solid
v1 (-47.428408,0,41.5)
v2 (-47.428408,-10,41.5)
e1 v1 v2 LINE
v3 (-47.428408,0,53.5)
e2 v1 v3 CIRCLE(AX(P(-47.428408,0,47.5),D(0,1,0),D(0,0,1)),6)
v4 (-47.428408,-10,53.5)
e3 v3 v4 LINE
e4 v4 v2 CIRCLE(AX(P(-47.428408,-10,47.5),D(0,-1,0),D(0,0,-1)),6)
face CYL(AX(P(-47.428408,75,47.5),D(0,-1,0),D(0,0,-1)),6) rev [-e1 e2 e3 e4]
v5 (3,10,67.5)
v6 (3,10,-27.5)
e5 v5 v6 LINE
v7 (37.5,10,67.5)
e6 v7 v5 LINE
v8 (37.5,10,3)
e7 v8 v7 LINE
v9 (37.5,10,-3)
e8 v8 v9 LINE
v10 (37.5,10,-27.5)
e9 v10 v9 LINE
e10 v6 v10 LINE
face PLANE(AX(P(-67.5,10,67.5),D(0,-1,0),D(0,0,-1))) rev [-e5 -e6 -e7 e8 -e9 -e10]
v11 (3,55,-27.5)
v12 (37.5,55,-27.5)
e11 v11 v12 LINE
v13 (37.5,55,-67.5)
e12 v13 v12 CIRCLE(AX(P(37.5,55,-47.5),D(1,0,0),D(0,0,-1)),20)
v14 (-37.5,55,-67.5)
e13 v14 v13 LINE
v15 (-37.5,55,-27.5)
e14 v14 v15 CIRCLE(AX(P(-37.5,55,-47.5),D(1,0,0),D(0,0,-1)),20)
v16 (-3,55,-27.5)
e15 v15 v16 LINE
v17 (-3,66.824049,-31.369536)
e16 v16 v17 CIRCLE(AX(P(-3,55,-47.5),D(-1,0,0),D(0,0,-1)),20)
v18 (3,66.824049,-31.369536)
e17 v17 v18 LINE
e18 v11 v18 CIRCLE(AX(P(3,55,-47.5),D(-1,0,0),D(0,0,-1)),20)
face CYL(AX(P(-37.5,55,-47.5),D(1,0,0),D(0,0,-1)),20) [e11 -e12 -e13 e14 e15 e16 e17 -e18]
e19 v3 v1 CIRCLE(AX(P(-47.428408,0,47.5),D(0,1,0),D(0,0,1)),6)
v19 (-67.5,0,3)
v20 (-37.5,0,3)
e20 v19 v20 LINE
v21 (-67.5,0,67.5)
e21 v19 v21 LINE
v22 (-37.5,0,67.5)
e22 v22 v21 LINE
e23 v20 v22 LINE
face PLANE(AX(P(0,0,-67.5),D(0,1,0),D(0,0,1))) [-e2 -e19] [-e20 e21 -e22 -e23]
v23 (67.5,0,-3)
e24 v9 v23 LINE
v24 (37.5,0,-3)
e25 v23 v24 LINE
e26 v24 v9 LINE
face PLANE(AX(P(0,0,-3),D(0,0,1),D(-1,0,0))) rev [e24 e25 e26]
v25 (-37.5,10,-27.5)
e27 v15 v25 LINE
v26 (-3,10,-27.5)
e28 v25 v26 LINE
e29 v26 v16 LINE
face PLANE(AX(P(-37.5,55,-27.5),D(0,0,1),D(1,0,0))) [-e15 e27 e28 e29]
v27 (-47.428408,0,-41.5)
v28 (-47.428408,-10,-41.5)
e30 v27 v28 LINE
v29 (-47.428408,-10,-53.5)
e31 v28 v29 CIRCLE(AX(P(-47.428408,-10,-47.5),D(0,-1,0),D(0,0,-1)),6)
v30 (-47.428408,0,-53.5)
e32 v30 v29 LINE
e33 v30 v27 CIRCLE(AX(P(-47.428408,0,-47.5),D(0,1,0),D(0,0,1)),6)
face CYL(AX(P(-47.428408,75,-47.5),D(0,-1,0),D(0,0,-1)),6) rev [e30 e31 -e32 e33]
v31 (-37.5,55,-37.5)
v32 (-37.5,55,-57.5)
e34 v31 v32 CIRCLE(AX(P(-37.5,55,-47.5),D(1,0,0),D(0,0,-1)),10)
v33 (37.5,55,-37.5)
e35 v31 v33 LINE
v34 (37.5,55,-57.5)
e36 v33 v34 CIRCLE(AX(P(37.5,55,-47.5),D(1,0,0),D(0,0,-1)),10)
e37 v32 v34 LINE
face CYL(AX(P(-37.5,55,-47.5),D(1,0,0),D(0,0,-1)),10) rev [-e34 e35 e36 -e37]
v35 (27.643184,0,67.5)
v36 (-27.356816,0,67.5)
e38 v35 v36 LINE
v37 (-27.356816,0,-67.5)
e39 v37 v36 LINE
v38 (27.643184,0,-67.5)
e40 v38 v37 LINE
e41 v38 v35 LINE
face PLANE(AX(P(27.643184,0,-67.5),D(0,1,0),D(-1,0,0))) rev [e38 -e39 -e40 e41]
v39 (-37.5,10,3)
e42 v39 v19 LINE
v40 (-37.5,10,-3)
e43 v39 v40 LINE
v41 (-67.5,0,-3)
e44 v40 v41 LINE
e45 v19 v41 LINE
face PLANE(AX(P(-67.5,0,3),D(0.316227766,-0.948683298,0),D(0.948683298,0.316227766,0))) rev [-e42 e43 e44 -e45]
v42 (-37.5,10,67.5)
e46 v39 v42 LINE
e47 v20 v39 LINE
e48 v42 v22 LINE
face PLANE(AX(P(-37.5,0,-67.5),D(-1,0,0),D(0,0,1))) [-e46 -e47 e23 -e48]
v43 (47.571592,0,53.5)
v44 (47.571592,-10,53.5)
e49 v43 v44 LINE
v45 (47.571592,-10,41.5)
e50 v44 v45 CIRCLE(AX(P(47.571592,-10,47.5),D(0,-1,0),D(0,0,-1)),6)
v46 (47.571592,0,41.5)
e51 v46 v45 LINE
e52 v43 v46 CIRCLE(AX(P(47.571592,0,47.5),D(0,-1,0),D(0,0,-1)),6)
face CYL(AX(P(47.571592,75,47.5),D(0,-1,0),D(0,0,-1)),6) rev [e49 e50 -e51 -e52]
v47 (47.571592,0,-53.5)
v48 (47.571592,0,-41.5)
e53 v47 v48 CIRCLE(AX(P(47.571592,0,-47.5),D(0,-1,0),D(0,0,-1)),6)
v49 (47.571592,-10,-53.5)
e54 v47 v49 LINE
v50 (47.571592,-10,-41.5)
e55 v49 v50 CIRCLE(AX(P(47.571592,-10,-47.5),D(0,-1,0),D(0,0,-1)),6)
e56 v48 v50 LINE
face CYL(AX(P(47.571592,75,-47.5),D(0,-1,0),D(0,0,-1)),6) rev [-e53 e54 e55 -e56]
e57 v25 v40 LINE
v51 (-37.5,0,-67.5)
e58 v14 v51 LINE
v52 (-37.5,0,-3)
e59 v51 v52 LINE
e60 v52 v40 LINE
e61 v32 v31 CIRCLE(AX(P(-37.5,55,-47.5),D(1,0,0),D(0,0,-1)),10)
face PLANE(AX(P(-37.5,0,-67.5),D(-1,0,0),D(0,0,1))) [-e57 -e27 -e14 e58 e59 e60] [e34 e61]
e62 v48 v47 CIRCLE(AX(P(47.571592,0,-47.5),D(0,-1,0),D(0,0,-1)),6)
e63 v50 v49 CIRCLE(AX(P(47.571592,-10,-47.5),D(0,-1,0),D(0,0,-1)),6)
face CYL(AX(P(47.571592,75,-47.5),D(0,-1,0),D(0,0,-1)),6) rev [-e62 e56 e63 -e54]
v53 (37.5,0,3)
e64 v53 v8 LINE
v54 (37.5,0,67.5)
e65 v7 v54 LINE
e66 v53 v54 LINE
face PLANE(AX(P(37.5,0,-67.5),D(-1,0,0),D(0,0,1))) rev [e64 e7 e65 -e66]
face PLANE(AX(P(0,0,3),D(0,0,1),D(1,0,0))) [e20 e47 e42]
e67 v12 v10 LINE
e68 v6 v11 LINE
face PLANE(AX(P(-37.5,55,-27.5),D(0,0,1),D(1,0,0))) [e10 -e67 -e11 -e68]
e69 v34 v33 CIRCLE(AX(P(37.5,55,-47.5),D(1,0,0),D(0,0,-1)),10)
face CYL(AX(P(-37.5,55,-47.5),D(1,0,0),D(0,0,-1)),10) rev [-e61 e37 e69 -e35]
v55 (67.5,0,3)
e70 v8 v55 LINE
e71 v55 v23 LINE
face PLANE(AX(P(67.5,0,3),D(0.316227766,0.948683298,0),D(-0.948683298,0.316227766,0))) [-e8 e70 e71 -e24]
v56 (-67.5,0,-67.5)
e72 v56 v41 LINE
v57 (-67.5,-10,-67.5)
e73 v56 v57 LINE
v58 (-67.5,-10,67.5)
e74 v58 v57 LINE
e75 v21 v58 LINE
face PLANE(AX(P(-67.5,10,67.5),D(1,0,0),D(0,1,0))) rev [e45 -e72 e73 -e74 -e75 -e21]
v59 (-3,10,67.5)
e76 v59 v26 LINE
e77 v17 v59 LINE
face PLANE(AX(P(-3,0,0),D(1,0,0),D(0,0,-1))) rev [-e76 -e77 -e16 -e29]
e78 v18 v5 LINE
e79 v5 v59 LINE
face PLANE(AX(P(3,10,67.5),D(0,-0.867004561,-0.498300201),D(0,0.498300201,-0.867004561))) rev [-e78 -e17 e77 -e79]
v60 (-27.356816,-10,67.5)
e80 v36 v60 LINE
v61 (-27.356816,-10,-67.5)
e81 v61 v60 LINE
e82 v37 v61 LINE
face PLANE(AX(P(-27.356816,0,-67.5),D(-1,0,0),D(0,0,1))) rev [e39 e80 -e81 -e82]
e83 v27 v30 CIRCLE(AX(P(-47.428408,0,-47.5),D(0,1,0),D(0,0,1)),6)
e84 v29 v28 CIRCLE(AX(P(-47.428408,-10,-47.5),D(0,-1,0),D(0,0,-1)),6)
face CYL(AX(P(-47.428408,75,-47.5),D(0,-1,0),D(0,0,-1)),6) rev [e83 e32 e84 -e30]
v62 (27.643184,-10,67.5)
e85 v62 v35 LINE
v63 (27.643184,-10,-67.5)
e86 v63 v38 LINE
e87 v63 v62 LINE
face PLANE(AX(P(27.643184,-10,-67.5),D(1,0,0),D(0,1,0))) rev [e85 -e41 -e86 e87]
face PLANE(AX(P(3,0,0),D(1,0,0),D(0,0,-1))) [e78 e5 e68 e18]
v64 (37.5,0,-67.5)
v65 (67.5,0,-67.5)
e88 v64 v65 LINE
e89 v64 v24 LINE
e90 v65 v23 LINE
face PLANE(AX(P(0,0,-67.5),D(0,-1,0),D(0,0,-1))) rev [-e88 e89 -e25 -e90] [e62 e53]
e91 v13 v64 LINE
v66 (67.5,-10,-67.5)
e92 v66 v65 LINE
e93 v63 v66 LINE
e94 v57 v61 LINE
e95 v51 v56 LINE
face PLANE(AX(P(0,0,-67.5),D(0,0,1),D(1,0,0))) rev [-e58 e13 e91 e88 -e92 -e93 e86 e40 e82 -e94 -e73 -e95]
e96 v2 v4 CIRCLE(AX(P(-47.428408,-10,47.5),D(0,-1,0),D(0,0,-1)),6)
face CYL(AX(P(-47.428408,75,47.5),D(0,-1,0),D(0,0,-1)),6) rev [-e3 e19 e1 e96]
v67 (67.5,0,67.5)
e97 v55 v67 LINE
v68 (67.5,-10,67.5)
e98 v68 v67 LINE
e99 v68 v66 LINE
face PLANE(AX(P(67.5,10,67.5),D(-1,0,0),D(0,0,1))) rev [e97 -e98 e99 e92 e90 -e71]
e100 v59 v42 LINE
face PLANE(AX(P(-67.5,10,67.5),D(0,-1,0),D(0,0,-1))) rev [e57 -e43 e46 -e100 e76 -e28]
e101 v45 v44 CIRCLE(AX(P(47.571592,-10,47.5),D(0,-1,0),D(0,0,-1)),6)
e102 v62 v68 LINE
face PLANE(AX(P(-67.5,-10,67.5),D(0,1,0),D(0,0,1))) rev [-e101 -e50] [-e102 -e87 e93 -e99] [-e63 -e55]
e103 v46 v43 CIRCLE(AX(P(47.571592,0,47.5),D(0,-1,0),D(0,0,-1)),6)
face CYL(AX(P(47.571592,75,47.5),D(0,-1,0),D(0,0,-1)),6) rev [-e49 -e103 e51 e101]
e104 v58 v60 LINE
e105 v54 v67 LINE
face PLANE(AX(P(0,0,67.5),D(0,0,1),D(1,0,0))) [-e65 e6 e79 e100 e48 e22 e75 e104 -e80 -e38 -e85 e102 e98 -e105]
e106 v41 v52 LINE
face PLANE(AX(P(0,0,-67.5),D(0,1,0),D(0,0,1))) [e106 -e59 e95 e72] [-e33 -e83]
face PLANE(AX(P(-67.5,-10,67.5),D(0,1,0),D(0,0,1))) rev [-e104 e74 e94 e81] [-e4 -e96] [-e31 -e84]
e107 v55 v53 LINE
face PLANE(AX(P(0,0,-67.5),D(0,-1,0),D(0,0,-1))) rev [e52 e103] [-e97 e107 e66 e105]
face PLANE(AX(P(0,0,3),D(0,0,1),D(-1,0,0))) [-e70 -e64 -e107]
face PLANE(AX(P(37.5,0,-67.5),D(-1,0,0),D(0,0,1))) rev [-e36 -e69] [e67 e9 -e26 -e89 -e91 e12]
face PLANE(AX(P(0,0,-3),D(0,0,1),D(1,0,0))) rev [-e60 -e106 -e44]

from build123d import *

# Parameters (mm, degrees)
BASE_PLATE_SKETCH_W     = 135
BASE_PLATE_SKETCH_H     = 20
BASE_PLATE_DEPTH        = 67.5
BOTTOM_CHANNEL_DEPTH    = 152.265495074
TOP_RECESS_SKETCH_W     = 30
TOP_RECESS_SKETCH_H     = 10
TOP_RECESS_DEPTH        = 152.265495074
UPRIGHT_LUG_SKETCH_R    = 10
UPRIGHT_LUG_DEPTH       = 75
SIDE_GUSSET_DEPTH       = 3
CENTRE_START            = -37.5
CENTRE_RIB_DEPTH        = 3
MOUNTING_HOLES_SKETCH_R = 6
MOUNTING_HOLES_12_DEPTH = 128.818230312


with BuildPart() as part:
    # Base Plate Sketch → Base Plate (new, symmetric)
    with BuildSketch(Plane.XY):
        Rectangle(BASE_PLATE_SKETCH_W, BASE_PLATE_SKETCH_H)
    extrude(amount=BASE_PLATE_DEPTH, both=True)

    # Bottom Channel Sketch → Bottom Channel (cut, through all)
    with BuildSketch(Plane.XY.offset(67.5)):
        Polygon((27.643184154, 0), (0, 0), (-27.356815846, 0), (-27.356815846, -10), (27.643184154, -10), align=None)
    extrude(amount=-BOTTOM_CHANNEL_DEPTH, mode=Mode.SUBTRACT)

    # Top Recess Sketch → Top Recess (cut, through all)
    with BuildSketch(Plane.XY.offset(67.5)):
        with Locations((-52.5, 5)):
            Rectangle(TOP_RECESS_SKETCH_W, TOP_RECESS_SKETCH_H)
        with Locations((52.5, 5)):
            Rectangle(TOP_RECESS_SKETCH_W, TOP_RECESS_SKETCH_H)
    extrude(amount=-TOP_RECESS_DEPTH, mode=Mode.SUBTRACT)

    # Upright Lug Sketch → Upright Lug (add)
    with BuildSketch(Plane(origin=(37.5, 0, 0), x_dir=(0, 0, -1), z_dir=(1, 0, 0))):
        with BuildLine():
            Line((67.5, 10), (67.5, 55))
            ThreePointArc((67.5, 55), (47.5, 75), (27.5, 55))
            Line((27.5, 55), (27.5, 10))
            Line((27.5, 10), (67.5, 10))
        make_face()
        with Locations((47.5, 55)):
            Circle(UPRIGHT_LUG_SKETCH_R, mode=Mode.SUBTRACT)
    extrude(amount=-UPRIGHT_LUG_DEPTH)

    # Side Gusset Sketch → Side Gusset (add, symmetric)
    with BuildSketch(Plane.XY):
        Polygon((-67.5, 0), (-37.5, 10), (-37.5, 0), align=None)
    side_gusset = extrude(amount=SIDE_GUSSET_DEPTH, both=True)

    # Side Gusset Mirror: Side Gusset across plane
    add(side_gusset.mirror(Plane(origin=(0, 0, 0), x_dir=(0, 0, 1), z_dir=(1, 0, 0))))

    # Centre Rib Sketch → Centre Rib (add, symmetric)
    with BuildSketch(Plane(origin=(37.5, 0, 0), x_dir=(0, 0, -1), z_dir=(1, 0, 0)).offset(CENTRE_START)):
        Polygon((-67.5, 10), (35.500032612, 69.198001073), (35.500032612, 10), (29.449687004, 10), align=None)
    extrude(amount=CENTRE_RIB_DEPTH, both=True)

    # Mounting Holes Sketch → Mounting Holes Ø12 (cut, through all)
    with BuildSketch(Plane.XZ.offset(10)):
        with Locations(Location((47.571592077, -47.5, 0), (0, 0, 270))):
            Circle(MOUNTING_HOLES_SKETCH_R)
        with Locations(Location((-47.428407923, -47.5, 0), (0, 0, 270))):
            Circle(MOUNTING_HOLES_SKETCH_R)
        with Locations(Location((-47.428407923, 47.5, 0), (0, 0, 270))):
            Circle(MOUNTING_HOLES_SKETCH_R)
        with Locations(Location((47.571592077, 47.5, 0), (0, 0, 270))):
            Circle(MOUNTING_HOLES_SKETCH_R)
    extrude(amount=-MOUNTING_HOLES_12_DEPTH, mode=Mode.SUBTRACT)


solid = part.part
